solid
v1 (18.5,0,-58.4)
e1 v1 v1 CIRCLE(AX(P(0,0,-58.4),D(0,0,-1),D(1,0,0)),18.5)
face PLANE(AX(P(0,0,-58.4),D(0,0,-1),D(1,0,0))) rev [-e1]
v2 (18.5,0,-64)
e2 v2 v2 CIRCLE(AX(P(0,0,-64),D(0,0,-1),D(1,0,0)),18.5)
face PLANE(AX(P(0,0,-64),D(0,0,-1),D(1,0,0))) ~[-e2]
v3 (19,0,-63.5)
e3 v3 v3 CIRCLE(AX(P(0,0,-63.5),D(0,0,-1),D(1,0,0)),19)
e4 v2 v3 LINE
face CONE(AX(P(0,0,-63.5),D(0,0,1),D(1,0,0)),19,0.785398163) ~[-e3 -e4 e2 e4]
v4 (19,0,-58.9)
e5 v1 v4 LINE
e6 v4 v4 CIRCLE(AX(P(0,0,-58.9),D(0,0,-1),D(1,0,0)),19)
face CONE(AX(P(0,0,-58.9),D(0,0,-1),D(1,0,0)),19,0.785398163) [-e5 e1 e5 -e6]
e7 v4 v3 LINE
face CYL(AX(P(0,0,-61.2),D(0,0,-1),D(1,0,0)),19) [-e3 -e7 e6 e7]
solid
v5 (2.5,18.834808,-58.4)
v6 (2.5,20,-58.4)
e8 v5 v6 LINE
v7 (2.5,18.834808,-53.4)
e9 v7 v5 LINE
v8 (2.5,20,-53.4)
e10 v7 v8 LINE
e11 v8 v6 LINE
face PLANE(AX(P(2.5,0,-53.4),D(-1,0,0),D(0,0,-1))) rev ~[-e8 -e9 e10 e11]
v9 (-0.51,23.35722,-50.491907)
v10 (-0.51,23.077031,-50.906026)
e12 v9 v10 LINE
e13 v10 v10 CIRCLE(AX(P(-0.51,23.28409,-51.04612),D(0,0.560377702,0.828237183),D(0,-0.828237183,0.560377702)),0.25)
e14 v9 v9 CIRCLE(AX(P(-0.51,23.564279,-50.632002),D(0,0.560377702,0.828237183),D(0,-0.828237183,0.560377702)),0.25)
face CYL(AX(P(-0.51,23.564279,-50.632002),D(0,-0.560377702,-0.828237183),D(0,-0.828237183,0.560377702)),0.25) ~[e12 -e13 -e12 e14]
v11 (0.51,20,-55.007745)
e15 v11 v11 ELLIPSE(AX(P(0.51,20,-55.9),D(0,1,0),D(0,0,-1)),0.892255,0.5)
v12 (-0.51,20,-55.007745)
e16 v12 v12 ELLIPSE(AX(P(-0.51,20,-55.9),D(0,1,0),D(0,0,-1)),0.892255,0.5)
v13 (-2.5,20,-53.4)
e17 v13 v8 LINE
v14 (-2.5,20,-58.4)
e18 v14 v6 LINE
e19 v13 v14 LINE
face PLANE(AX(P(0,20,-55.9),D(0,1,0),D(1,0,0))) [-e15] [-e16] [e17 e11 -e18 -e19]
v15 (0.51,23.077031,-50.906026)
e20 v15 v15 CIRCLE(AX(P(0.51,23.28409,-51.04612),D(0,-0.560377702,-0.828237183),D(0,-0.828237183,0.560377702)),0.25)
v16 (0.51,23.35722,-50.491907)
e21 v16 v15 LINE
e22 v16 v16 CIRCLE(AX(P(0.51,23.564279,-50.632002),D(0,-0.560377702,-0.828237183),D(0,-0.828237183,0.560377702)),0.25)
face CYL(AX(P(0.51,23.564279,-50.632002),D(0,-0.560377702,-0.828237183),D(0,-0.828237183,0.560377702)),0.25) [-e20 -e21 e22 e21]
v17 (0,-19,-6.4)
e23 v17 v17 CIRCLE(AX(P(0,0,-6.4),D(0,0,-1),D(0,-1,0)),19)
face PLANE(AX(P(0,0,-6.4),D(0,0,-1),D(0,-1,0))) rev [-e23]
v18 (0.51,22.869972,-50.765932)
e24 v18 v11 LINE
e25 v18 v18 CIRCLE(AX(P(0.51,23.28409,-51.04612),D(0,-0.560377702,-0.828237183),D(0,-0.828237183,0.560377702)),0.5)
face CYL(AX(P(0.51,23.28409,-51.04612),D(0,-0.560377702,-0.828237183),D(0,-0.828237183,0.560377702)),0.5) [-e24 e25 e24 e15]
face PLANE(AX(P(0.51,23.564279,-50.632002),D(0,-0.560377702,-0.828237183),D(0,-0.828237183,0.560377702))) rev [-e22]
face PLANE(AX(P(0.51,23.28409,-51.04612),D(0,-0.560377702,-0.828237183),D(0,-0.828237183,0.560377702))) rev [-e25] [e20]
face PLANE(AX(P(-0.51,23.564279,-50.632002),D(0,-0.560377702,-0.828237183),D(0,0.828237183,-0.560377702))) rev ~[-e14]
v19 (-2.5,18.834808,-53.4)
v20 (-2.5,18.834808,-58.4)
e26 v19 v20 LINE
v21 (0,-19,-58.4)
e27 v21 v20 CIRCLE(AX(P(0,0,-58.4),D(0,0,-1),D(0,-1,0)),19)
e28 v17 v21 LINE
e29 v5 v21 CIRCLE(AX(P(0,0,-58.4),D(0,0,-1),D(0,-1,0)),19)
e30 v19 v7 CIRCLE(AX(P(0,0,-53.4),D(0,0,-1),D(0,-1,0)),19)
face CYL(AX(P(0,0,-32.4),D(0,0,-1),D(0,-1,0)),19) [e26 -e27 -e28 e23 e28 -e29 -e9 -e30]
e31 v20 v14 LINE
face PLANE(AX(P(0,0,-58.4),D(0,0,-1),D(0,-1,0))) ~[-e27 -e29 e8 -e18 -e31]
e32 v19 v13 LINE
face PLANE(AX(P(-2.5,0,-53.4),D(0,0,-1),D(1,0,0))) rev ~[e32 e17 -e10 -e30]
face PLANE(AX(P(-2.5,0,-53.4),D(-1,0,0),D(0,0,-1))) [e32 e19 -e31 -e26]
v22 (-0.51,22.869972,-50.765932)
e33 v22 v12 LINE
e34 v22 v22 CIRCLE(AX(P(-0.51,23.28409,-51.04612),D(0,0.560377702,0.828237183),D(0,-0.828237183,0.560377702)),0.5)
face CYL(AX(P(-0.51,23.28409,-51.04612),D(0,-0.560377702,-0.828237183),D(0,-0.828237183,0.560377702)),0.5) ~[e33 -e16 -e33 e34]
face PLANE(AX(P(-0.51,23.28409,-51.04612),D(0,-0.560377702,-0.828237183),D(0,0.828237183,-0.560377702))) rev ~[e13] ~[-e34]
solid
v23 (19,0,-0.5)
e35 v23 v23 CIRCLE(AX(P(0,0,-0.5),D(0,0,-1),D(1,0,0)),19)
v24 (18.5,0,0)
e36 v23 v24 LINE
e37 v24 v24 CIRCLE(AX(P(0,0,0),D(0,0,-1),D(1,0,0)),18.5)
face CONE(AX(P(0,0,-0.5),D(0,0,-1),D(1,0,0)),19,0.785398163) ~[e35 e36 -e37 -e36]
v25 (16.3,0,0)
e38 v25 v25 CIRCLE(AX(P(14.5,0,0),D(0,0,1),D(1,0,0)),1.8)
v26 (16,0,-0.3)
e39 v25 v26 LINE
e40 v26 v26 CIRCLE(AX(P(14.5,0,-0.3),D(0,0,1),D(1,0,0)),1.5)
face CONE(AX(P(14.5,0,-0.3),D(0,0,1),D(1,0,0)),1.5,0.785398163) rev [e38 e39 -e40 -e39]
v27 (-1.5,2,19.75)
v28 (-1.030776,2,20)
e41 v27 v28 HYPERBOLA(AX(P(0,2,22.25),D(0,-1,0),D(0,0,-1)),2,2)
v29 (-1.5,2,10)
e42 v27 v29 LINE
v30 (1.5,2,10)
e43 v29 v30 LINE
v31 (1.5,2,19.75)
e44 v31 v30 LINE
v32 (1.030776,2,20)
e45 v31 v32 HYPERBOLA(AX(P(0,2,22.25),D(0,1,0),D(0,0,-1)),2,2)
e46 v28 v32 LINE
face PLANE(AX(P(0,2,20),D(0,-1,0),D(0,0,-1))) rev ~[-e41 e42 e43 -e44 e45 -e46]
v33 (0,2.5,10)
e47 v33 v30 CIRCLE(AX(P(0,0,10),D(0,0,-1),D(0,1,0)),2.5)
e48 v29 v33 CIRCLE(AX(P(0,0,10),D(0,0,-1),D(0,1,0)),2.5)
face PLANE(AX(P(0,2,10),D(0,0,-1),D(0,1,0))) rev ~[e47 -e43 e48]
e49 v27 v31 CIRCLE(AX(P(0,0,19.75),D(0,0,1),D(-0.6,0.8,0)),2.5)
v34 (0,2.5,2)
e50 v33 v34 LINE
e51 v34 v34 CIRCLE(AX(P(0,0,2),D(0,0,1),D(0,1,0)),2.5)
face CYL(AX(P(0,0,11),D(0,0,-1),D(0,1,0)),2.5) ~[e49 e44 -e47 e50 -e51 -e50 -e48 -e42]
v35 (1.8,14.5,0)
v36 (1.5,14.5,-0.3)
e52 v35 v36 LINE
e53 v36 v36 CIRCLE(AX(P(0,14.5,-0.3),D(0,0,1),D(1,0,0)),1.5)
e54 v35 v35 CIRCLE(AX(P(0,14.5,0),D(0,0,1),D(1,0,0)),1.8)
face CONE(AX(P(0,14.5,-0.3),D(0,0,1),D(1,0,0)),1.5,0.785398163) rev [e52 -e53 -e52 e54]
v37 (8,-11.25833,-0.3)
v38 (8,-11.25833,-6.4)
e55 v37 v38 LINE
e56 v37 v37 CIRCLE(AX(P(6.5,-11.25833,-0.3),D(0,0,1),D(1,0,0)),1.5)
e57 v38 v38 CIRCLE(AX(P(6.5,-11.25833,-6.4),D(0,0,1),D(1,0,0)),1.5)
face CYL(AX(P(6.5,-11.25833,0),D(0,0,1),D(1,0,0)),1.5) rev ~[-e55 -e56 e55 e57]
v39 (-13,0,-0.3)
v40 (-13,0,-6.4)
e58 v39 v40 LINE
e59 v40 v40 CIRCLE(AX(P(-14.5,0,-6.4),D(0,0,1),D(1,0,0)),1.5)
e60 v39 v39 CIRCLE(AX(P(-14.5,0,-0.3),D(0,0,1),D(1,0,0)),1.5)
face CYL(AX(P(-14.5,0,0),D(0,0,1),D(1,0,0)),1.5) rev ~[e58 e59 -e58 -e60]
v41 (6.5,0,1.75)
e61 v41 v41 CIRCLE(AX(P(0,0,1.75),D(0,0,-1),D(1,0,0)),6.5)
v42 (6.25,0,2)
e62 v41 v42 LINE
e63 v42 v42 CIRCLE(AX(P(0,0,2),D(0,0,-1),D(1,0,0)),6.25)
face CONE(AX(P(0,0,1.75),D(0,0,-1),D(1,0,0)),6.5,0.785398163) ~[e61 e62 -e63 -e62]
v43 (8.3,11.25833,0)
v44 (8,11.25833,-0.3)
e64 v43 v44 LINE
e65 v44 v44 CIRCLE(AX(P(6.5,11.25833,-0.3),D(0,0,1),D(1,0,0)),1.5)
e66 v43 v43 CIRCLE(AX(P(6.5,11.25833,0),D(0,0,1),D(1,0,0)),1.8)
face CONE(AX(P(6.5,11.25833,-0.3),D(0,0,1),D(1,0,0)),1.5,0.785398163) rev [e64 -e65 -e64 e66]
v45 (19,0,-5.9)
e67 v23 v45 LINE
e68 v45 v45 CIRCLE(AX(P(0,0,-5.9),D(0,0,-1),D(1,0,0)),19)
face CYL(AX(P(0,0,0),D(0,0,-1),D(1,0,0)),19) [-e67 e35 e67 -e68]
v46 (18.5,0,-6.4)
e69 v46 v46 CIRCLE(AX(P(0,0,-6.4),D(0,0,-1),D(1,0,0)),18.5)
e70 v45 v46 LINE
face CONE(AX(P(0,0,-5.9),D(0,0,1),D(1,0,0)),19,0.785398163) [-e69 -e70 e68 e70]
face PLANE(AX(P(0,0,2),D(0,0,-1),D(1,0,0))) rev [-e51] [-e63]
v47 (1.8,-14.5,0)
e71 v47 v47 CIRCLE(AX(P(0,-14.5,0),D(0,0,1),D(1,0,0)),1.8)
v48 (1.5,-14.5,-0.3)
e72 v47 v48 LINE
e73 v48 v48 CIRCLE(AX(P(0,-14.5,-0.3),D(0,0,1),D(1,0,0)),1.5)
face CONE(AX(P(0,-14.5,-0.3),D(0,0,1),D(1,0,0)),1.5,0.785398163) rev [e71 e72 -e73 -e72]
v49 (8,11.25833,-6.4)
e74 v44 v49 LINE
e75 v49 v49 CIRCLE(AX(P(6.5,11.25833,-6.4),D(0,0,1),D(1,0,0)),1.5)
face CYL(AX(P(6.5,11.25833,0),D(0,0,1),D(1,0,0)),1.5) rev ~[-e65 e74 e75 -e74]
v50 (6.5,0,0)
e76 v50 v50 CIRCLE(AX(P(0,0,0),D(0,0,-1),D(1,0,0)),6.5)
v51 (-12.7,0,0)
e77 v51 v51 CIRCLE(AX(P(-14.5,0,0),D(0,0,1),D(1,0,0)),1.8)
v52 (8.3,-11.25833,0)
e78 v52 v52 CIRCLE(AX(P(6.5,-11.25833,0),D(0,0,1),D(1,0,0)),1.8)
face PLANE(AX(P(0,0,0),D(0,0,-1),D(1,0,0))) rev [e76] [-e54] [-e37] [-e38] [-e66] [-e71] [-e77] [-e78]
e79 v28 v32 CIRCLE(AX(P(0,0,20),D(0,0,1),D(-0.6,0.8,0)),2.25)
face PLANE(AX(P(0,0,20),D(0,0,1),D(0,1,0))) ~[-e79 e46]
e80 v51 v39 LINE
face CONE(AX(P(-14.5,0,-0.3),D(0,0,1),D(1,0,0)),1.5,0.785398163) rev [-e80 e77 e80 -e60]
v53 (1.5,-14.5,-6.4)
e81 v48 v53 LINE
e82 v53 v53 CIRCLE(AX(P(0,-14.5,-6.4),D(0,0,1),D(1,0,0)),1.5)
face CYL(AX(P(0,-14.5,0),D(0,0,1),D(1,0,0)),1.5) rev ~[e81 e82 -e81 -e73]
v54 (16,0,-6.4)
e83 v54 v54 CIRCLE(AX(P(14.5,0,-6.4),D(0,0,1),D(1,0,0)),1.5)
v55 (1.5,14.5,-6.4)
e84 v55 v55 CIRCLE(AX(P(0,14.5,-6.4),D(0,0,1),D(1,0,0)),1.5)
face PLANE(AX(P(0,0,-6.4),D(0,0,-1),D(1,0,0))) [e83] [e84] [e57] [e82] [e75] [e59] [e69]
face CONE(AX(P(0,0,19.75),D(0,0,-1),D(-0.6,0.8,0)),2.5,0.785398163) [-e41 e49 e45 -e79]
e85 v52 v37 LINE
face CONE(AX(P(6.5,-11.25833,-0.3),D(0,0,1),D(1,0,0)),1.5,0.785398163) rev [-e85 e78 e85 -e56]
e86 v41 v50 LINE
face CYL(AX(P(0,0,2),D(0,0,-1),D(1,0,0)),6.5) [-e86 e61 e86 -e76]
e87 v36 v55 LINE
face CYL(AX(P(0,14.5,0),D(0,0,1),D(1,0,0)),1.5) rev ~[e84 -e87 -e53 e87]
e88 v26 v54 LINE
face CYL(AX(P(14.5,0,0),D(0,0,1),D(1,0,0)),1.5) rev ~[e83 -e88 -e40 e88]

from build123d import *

# Parameters (mm, degrees)
SKETCH_13_W         = 5.6
SKETCH_13_H         = 19
SKETCH_2_W          = 52
SKETCH_2_H          = 19
SKETCH_15_W         = 18
SKETCH_15_H         = 2.5
SKETCH_17_W         = 10
SKETCH_17_H         = 0.5
CUT_EXTRUDE_1_DEPTH = 5
SKETCH_9_W          = 5
SKETCH_9_H          = 5
EXTRUDE_1_DEPTH     = 20
CHAMFER_1_SIZE      = 0.5
CHAMFER_2_SIZE      = 0.5
CHAMFER_3_SIZE      = 0.25
SKETCH_18_R         = 1.5
CUT_EXTRUDE_2_DEPTH = 6.4
CHAMFER_4_SIZE      = 0.3


with BuildPart() as part:
    # 草图13 → 旋转9 (revolve)
    with BuildSketch(Plane(origin=(0, 0, 0), x_dir=(0, 0, -1), z_dir=(1, 0, 0)), mode=Mode.PRIVATE) as revolve_9_sk:
        Polygon((0, 19), (6.4, 19), (6.4, 0), (0, 0), (-2, 0), (-2, 6.5), (0, 6.5), align=None)
        with Locations((61.2, 9.5)):
            Rectangle(SKETCH_13_W, SKETCH_13_H)
    revolve(revolve_9_sk.sketch.rotate(Axis((0, 0, -58.4), (0, 0, -1)), 90), axis=Axis((0, 0, -58.4), (0, 0, -1)))

    # 草图15 → 旋转11 (revolve)
    with BuildSketch(Plane(origin=(0, 0, 0), x_dir=(0, 0, -1), z_dir=(1, 0, 0))):
        with Locations((-11, 1.25)):
            Rectangle(SKETCH_15_W, SKETCH_15_H)
    revolve(axis=Axis((0, 0, 2), (0, 0, 1)))

    # 草图17 → 切除-拉伸1 (cut, symmetric)
    with BuildSketch(Plane(origin=(0, 0, 0), x_dir=(0, 0, -1), z_dir=(1, 0, 0))):
        with Locations((-15, 2.25)):
            Rectangle(SKETCH_17_W, SKETCH_17_H)
    extrude(amount=CUT_EXTRUDE_1_DEPTH, both=True, mode=Mode.SUBTRACT)

    # 倒角1
    chamfer_1_edges = [part.edges().sort_by_distance(p)[0] for p in [
        (-19, 0, -58.4),
        (-19, 0, -64),
    ]]
    chamfer(chamfer_1_edges, length=CHAMFER_1_SIZE)

    # 倒角2
    chamfer_2_edges = [part.edges().sort_by_distance(p)[0] for p in [
        (-19, 0, -6.4),
        (-19, 0, 0),
    ]]
    chamfer(chamfer_2_edges, length=CHAMFER_2_SIZE)

    # 倒角3
    chamfer_3_edges = [part.edges().sort_by_distance(p)[0] for p in [
        (0, -2.5, 20),
        (-6.5, 0, 2),
    ]]
    chamfer(chamfer_3_edges, length=CHAMFER_3_SIZE)

    # 草图18 → 切除-拉伸2 (cut)
    with BuildSketch(Plane.XY):
        with Locations((0, 14.5)):
            Circle(SKETCH_18_R)
        with Locations((6.5, 11.258330249)):
            Circle(SKETCH_18_R)
        with Locations((6.5, -11.258330249)):
            Circle(SKETCH_18_R)
        with Locations((0, -14.5)):
            Circle(SKETCH_18_R)
        with Locations((14.5, 0)):
            Circle(SKETCH_18_R)
        with Locations((-14.5, 0)):
            Circle(SKETCH_18_R)
    extrude(amount=-CUT_EXTRUDE_2_DEPTH, mode=Mode.SUBTRACT)

    # 倒角4
    chamfer_4_edges = [part.edges().sort_by_distance(p)[0] for p in [
        (-1.5, 14.5, 0),
        (5, 11.258330249, 0),
        (5, -11.258330249, 0),
        (-1.5, -14.5, 0),
        (13, 0, 0),
        (-16, 0, 0),
    ]]
    chamfer(chamfer_4_edges, length=CHAMFER_4_SIZE)


with BuildPart() as body_2:
    # 草图2 → 旋转10 (revolve)
    with BuildSketch(Plane(origin=(0, 0, 0), x_dir=(0, 0, -1), z_dir=(1, 0, 0)), mode=Mode.PRIVATE) as revolve_10_sk:
        with Locations((32.4, 9.5)):
            Rectangle(SKETCH_2_W, SKETCH_2_H)
    revolve(revolve_10_sk.sketch.rotate(Axis((0, 0, -6.4), (0, 0, -1)), 180), axis=Axis((0, 0, -6.4), (0, 0, -1)))

    # 草图9 → 凸台-拉伸1 (add)
    with BuildSketch(Plane(origin=(0, 0, 0), x_dir=(1, 0, 0), z_dir=(0, 1, 0))):
        with Locations((0, 55.9)):
            Rectangle(SKETCH_9_W, SKETCH_9_H)
    extrude(amount=EXTRUDE_1_DEPTH)

    # 草图12 → 旋转12 (revolve)
    with BuildSketch(Plane(origin=(0.51, 0, 0), x_dir=(0, 0, -1), z_dir=(1, 0, 0))):
        Polygon((50.765931613, 22.869971904), (56.485742762, 19), (56.765931613, 19.414118591), (50.632001872, 23.564279347), (50.491907447, 23.357220051), (50.906026038, 23.0770312), align=None)
    revolve_12 = revolve(axis=Axis((0.51, 23.564279347, -50.632001872), (0, -0.5603777020527585, -0.8282371828420104)))

    # 镜向1: 旋转12 across plane
    add(revolve_12.mirror(Plane(origin=(0, 0, 0), x_dir=(0, 0, 1), z_dir=(1, 0, 0))))


solid = Compound([part.part, body_2.part])
